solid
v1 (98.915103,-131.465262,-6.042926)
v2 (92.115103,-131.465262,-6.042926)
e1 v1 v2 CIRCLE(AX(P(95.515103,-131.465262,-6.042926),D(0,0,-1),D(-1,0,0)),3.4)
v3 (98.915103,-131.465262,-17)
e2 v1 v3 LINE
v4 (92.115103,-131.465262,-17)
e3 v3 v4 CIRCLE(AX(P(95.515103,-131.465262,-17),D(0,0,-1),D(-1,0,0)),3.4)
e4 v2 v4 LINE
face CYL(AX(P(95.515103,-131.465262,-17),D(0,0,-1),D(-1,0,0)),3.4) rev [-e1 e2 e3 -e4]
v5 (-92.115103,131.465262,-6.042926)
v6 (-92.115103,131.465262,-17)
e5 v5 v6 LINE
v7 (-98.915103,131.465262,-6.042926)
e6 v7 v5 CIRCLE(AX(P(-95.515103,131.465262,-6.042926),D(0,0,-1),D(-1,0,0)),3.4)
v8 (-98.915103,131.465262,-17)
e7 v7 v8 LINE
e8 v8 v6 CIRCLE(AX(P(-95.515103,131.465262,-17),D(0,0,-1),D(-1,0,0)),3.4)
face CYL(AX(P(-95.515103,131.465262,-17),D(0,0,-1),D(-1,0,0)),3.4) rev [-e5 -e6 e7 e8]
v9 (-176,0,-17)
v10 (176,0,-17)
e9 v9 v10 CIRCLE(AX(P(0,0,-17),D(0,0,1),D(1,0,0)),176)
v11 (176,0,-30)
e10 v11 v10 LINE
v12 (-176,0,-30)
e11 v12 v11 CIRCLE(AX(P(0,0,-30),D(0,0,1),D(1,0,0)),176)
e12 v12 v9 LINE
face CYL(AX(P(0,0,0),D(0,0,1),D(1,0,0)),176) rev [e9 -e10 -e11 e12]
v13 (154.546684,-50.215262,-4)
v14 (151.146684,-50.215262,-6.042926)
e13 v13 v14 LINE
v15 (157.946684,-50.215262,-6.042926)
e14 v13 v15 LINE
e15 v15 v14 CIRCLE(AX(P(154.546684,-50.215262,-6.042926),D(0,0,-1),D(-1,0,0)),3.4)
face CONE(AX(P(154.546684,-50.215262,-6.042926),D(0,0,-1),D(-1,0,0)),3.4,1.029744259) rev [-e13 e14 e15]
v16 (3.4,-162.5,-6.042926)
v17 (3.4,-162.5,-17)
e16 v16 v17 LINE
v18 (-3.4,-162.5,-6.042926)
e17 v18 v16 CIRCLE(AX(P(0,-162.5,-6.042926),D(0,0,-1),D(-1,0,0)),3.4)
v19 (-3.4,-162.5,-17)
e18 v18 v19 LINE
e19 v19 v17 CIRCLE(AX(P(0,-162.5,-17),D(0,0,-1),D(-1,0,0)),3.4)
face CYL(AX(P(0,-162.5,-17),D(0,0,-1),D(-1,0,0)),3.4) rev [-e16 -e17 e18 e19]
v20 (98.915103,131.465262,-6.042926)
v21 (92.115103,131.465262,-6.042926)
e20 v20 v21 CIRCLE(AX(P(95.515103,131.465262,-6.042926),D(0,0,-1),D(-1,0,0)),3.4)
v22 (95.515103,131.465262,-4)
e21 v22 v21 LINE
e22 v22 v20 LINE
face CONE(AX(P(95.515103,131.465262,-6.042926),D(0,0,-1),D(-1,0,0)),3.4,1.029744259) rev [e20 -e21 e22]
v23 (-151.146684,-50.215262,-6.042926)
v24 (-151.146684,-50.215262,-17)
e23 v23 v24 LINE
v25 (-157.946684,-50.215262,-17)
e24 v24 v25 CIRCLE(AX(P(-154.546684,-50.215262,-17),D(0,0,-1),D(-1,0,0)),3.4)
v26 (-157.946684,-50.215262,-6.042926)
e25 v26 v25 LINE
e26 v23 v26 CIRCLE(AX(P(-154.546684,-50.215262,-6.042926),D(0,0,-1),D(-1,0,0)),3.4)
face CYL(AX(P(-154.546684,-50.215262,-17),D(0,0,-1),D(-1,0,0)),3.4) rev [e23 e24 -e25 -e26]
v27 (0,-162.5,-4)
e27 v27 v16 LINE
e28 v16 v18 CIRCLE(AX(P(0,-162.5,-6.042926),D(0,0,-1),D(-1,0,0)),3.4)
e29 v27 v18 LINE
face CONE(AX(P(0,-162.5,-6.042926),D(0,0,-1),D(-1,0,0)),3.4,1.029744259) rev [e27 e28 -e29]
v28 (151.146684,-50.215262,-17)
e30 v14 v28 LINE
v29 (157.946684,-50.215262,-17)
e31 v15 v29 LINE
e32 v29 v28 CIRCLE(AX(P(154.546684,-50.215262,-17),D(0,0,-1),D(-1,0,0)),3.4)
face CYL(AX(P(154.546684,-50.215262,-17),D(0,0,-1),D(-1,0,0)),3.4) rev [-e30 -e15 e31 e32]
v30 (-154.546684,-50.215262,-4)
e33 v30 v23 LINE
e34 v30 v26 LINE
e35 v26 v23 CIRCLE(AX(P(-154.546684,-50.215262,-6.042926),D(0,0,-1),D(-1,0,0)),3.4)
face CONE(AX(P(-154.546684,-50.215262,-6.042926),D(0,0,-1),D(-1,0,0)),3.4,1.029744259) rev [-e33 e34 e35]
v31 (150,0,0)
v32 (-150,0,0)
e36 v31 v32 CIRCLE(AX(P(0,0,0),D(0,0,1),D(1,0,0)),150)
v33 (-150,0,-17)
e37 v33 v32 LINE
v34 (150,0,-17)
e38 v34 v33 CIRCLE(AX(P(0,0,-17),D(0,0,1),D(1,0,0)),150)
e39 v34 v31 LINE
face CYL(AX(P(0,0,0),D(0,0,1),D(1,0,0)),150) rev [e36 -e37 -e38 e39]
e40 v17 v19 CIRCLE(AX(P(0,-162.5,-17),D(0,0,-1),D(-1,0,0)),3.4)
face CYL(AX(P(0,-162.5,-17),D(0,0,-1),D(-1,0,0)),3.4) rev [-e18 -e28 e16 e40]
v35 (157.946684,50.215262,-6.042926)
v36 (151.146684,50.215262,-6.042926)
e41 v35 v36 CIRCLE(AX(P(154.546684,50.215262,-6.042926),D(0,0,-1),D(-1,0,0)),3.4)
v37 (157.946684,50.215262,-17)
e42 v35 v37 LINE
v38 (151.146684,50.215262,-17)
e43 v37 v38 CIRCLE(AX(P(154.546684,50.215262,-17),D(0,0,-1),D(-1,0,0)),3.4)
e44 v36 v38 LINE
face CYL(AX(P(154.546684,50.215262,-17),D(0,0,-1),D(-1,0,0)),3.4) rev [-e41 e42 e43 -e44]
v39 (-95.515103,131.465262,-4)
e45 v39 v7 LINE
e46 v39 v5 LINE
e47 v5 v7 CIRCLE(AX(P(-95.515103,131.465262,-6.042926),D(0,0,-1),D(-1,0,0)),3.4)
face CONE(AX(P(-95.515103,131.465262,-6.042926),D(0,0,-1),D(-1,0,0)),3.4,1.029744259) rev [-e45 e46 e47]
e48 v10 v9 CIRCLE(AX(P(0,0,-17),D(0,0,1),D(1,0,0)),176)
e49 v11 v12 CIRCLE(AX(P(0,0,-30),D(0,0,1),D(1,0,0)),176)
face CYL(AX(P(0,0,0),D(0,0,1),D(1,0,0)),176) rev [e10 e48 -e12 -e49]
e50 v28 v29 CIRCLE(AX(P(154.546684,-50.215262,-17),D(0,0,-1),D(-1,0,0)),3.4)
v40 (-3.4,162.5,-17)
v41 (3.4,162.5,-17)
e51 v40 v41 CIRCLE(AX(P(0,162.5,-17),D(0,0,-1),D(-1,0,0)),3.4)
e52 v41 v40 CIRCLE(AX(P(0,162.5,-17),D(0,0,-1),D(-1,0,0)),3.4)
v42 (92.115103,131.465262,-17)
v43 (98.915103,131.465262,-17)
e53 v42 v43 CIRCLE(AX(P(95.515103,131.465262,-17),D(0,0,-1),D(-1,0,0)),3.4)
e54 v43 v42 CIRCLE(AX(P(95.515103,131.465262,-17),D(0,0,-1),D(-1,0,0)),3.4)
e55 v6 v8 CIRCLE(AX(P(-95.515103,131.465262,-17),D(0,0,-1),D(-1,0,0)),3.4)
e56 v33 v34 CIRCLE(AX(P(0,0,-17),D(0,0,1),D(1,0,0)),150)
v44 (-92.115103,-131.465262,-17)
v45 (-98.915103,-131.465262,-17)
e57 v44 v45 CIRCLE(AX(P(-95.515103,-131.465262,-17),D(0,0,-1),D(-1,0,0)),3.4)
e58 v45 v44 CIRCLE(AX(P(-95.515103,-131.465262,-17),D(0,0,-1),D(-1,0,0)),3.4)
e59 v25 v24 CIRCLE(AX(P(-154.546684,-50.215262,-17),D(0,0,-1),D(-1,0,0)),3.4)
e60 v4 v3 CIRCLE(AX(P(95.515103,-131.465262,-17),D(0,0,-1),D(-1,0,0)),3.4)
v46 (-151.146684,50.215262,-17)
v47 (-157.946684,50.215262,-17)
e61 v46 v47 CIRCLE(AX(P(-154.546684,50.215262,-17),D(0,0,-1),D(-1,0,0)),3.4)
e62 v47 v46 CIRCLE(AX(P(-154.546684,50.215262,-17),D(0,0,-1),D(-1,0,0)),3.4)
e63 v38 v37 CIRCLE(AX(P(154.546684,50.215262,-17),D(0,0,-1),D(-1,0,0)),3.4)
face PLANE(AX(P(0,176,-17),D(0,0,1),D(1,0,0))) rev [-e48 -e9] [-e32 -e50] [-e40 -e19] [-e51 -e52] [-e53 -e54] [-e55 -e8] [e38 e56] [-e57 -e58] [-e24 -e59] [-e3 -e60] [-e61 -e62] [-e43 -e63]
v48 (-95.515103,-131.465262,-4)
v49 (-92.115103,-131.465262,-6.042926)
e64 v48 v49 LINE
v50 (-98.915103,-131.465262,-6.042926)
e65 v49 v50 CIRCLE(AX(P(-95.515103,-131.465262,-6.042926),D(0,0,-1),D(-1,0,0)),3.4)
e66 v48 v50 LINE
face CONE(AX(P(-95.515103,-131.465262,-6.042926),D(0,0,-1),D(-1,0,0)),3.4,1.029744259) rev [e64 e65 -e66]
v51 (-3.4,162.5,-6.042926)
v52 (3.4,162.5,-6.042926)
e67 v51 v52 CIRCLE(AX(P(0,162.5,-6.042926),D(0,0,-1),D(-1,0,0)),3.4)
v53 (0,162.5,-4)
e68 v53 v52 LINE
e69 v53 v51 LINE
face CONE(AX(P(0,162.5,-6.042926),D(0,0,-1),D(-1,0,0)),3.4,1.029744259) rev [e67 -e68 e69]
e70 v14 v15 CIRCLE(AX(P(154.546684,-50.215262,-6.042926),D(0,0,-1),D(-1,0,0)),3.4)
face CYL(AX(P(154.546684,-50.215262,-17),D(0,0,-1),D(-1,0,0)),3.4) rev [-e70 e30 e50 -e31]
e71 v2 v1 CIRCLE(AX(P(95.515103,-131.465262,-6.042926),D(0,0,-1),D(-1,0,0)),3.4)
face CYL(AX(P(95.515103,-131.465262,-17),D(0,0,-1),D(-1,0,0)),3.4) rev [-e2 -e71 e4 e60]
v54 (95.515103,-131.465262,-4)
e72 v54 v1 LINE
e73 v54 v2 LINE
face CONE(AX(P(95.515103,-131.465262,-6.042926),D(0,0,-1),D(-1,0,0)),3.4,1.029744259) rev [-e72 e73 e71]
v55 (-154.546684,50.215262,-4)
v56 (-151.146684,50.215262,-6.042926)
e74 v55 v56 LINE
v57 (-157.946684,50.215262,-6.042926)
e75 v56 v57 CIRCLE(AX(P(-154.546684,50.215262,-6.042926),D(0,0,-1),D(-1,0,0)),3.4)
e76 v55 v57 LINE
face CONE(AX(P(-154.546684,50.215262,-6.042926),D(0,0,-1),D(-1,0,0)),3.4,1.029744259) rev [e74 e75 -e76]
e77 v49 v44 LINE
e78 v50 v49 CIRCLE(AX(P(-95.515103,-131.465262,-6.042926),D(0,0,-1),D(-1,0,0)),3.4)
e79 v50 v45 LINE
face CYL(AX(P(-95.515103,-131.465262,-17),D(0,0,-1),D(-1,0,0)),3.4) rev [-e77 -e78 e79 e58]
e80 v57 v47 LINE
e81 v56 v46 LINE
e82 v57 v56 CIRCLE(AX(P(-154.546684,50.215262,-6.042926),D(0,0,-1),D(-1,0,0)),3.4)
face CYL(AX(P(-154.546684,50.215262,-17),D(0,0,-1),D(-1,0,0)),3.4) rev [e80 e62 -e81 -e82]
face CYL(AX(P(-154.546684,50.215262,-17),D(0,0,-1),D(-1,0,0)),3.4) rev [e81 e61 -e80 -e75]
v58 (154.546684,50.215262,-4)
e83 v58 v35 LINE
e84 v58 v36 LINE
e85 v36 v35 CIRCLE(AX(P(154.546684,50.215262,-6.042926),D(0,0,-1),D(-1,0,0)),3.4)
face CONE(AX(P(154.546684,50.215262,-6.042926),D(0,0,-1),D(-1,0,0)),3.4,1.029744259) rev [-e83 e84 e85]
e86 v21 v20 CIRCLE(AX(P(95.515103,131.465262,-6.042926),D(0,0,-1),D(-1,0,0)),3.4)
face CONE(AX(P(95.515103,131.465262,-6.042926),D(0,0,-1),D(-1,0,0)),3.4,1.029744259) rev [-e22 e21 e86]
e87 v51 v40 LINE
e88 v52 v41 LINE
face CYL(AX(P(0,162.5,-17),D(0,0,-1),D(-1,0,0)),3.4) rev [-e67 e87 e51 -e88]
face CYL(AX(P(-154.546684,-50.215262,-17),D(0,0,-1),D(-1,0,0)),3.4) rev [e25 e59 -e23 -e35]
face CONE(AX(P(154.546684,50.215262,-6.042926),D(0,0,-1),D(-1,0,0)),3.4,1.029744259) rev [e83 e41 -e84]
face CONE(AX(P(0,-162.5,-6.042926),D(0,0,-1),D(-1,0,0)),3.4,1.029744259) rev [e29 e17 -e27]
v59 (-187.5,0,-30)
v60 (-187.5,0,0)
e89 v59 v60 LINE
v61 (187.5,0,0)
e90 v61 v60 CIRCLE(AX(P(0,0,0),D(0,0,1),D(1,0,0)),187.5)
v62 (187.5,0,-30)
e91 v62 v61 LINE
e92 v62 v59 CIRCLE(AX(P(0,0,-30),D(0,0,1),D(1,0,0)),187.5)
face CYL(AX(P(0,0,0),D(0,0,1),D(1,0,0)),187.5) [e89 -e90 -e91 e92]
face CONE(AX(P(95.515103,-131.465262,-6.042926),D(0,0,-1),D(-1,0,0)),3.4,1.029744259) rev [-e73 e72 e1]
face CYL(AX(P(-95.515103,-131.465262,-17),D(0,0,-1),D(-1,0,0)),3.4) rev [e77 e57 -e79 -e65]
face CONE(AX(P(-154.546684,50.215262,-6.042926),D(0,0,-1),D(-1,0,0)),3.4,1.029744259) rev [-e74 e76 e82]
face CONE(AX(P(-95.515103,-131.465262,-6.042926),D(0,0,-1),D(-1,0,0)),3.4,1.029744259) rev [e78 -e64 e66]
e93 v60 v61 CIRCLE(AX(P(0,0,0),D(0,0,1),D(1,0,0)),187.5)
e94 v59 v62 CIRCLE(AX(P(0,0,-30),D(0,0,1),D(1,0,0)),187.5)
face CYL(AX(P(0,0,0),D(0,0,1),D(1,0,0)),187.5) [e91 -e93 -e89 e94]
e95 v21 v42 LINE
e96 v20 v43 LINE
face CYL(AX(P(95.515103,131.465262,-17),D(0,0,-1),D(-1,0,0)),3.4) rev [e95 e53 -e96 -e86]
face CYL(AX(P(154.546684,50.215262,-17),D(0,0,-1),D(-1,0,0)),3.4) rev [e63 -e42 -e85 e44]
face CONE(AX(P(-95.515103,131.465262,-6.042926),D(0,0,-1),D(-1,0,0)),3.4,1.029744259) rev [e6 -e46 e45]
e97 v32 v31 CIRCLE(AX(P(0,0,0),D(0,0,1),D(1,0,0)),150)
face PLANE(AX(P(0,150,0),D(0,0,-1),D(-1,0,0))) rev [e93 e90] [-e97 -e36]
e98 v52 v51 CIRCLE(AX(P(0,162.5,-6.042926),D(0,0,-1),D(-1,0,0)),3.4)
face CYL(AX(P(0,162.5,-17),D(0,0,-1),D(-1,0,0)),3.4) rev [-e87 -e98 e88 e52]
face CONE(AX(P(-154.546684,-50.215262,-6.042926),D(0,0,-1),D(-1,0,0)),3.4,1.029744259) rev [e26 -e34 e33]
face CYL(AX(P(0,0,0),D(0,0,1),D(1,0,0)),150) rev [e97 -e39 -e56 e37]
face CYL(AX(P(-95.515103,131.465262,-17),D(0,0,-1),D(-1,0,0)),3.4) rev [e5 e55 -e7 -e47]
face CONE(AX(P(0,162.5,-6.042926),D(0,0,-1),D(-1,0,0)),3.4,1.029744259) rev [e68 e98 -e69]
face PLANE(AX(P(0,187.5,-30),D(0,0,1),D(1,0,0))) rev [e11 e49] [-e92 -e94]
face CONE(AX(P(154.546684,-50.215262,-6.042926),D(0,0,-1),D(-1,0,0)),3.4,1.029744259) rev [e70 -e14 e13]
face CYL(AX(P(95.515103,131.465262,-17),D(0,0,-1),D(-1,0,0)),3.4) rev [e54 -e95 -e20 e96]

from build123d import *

# Parameters (mm, degrees)
M8_TAPPED_HOLE1_D     = 6.8
M8_TAPPED_HOLE1_DEPTH = 10.957073895
M8_TAPPED_HOLE1_TIP   = 2.042926105


with BuildPart() as part:
    # Sketch1 → Revolve1 (revolve)
    with BuildSketch(Plane(origin=(0, 0, 0), x_dir=(0, 0, -1), z_dir=(1, 0, 0)), mode=Mode.PRIVATE) as revolve1_sk:
        Polygon((0, 150), (0, 187.5), (30, 187.5), (30, 176), (17, 176), (17, 150), align=None)
    revolve(revolve1_sk.sketch.rotate(Axis((0, 0, 0), (0, 0, -1)), 90), axis=Axis((0, 0, 0), (0, 0, -1)))

    # M8 Tapped Hole1
    with Locations(Plane(origin=(0, 0, -17), x_dir=(-1, 0, 0), z_dir=(0, 0, -1))):
        with Locations((0, 162.5), (95.515103498, 131.465261586), (154.546683898, 50.215261586), (154.546683898, -50.215261586), (95.515103498, -131.465261586), (0, -162.5), (-95.515103498, -131.465261586), (-154.546683898, -50.215261586), (-154.546683898, 50.215261586), (-95.515103498, 131.465261586)):
            Hole(M8_TAPPED_HOLE1_D / 2, depth=M8_TAPPED_HOLE1_DEPTH)
            with Locations((0, 0, -(M8_TAPPED_HOLE1_DEPTH + M8_TAPPED_HOLE1_TIP / 2))):  # 118° drill point
                Cone(0, M8_TAPPED_HOLE1_D / 2, M8_TAPPED_HOLE1_TIP, mode=Mode.SUBTRACT)


solid = part.part
